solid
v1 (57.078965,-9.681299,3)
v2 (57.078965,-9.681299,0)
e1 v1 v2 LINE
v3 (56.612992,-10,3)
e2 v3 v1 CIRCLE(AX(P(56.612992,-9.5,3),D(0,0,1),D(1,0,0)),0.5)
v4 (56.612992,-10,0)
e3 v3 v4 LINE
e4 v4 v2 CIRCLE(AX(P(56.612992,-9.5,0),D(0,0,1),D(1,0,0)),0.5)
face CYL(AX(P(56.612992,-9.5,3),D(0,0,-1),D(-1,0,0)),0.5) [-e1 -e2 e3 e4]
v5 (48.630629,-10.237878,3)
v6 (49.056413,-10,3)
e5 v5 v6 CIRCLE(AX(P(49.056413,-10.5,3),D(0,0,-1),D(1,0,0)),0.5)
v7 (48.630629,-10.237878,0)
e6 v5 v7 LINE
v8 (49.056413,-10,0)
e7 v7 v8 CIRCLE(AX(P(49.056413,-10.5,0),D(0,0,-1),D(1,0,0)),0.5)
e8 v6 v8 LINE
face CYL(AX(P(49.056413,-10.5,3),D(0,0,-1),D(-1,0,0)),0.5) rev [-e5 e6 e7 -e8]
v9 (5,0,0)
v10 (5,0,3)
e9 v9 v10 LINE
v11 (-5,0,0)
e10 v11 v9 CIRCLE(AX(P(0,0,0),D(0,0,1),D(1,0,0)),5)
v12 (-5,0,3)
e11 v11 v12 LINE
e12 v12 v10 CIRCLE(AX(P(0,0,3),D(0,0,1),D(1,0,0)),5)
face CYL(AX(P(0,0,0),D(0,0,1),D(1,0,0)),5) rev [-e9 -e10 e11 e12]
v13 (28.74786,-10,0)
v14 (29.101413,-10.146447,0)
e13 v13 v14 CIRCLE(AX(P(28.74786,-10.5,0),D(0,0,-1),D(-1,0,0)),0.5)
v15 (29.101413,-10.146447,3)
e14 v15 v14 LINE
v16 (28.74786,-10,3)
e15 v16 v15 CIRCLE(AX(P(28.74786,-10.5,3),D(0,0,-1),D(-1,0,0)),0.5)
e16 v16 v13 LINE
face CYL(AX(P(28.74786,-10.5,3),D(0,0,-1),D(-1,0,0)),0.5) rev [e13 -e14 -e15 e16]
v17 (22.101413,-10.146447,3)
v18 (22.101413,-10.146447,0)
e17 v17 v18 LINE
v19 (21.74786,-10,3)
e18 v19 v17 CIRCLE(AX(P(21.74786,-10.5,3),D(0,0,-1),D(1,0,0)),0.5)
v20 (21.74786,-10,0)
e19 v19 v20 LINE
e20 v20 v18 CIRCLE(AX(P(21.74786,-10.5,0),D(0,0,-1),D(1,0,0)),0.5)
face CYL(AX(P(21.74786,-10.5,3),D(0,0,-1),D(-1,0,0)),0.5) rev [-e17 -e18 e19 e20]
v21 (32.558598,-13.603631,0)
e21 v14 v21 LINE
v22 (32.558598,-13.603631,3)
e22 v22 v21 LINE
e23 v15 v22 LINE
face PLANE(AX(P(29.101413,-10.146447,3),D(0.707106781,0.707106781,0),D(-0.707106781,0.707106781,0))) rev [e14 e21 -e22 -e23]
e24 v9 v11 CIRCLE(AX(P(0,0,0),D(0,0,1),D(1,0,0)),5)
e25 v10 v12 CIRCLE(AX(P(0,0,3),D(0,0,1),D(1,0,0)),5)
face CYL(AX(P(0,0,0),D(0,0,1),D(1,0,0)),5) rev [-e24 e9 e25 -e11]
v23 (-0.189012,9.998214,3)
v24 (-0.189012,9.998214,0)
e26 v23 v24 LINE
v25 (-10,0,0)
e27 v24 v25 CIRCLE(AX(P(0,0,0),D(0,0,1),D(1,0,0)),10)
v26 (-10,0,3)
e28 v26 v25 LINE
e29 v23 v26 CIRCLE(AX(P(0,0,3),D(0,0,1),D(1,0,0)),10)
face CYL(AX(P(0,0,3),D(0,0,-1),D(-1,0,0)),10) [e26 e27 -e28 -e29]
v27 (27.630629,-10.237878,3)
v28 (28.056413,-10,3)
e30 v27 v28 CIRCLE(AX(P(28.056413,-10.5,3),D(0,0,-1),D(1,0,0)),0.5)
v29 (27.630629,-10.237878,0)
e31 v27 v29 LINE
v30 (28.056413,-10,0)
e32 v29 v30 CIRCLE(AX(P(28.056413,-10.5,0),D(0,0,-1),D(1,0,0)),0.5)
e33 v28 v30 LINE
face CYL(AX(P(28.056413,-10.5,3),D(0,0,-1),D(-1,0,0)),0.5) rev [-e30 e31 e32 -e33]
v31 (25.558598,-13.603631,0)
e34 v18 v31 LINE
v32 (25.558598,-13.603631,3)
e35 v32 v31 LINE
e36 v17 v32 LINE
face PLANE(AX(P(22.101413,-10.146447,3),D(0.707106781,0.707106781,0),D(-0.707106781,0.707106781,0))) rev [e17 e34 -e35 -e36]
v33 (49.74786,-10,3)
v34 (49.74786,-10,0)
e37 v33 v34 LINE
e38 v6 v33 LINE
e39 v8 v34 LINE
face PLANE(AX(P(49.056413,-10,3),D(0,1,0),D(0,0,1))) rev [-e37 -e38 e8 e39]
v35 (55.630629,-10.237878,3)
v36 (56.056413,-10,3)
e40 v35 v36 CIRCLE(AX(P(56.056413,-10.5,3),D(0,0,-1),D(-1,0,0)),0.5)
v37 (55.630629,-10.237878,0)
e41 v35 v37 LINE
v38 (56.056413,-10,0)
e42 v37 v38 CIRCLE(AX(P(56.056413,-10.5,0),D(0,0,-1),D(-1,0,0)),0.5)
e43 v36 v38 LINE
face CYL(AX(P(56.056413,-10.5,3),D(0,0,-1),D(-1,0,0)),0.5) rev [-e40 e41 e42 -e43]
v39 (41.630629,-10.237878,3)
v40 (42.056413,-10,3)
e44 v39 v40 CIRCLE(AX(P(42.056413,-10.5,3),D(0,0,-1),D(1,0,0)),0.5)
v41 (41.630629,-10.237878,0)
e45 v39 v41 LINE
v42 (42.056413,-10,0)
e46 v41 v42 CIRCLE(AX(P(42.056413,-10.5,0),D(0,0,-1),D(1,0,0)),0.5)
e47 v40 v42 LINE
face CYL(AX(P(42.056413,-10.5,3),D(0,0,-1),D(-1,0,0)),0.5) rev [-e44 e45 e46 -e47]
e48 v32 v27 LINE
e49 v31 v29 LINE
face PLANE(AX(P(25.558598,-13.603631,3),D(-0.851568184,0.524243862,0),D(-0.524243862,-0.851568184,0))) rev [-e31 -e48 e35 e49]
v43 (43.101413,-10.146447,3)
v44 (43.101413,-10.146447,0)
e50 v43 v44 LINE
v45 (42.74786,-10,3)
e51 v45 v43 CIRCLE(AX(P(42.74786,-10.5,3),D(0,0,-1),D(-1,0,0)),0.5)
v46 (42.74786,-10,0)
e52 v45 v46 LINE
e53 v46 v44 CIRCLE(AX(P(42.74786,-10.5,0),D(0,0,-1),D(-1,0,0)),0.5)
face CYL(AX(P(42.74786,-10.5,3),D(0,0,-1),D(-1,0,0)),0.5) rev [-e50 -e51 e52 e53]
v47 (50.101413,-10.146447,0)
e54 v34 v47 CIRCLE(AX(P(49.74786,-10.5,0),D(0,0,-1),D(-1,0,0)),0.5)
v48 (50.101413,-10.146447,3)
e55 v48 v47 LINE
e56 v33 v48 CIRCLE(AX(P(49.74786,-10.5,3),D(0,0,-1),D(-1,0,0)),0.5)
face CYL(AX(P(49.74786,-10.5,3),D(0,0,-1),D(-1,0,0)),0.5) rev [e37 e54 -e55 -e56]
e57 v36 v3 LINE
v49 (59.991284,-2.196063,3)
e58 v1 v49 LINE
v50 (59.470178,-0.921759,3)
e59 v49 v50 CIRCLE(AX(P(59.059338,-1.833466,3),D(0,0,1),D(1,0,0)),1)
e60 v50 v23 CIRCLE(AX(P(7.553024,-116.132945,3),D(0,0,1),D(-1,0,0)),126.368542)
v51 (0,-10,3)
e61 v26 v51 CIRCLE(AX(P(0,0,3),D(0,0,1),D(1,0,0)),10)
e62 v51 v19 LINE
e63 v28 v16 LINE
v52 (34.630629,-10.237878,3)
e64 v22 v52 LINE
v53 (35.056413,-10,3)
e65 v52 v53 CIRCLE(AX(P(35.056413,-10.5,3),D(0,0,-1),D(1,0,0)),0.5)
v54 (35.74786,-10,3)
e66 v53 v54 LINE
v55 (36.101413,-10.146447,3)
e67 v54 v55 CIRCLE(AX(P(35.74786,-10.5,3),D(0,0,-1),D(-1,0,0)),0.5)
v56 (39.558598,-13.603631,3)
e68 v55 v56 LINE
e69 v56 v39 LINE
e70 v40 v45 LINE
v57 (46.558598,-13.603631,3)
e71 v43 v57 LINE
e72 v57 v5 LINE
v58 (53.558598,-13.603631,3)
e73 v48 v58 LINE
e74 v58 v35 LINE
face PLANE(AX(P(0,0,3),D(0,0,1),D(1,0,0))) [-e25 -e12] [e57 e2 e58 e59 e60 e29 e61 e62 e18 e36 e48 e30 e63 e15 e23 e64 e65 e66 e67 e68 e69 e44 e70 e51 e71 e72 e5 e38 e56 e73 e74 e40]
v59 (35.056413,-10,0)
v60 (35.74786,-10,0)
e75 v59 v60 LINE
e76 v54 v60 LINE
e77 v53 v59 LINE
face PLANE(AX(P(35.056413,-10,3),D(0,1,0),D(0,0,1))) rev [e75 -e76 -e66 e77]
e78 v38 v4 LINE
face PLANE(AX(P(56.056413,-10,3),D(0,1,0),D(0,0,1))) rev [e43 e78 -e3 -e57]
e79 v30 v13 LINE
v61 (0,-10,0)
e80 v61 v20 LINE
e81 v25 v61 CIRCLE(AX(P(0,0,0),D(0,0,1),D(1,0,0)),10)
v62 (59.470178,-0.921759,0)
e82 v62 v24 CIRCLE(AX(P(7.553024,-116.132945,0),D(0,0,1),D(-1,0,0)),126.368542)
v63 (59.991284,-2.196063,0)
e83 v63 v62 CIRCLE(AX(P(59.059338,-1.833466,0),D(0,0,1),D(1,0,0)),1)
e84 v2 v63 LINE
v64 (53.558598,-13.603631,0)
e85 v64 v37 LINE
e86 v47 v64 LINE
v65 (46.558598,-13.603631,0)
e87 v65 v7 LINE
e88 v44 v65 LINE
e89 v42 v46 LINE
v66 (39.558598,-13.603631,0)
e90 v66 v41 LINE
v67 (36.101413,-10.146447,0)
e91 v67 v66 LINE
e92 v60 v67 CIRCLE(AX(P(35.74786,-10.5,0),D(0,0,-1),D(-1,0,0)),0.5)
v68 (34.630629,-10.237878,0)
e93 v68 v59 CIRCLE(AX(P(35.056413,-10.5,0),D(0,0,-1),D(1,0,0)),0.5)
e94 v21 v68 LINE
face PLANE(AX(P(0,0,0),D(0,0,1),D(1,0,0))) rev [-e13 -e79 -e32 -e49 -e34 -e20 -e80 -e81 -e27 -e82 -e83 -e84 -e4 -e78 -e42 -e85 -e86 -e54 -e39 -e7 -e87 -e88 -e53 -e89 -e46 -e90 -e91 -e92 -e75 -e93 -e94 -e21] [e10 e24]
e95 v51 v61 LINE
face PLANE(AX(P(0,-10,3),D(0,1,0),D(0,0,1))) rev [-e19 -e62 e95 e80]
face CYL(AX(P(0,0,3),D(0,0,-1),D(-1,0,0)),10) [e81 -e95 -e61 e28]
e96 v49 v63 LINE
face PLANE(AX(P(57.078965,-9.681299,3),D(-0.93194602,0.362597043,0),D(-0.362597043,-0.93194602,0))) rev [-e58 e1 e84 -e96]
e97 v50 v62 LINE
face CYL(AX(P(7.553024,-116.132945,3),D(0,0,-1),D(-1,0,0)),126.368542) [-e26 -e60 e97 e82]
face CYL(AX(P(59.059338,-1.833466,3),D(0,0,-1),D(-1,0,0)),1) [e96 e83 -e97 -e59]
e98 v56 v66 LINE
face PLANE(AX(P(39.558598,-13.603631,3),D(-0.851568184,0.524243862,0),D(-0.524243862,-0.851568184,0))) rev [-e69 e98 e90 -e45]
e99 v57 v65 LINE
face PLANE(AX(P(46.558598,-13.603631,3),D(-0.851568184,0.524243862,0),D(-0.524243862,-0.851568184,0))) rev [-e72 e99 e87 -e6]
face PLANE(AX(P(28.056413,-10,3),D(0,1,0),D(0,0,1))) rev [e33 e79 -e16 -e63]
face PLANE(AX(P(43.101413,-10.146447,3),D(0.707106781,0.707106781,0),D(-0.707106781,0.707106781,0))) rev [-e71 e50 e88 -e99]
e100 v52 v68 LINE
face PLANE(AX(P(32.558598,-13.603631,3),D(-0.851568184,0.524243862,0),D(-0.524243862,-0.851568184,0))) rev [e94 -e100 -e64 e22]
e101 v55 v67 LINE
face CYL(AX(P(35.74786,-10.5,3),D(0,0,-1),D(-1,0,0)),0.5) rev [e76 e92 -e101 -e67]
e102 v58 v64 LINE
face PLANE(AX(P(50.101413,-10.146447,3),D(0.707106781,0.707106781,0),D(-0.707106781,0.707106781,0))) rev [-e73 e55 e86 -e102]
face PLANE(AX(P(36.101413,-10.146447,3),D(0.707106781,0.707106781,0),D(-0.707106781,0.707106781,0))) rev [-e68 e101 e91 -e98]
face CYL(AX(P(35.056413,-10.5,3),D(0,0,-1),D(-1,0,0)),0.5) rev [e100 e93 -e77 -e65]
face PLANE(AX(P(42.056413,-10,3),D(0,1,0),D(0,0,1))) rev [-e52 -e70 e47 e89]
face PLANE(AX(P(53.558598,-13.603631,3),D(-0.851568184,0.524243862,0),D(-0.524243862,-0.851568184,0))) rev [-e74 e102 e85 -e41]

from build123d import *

# Parameters (mm, degrees)
BOSS_EXTRUDE3_DEPTH = 3
SKETCH4_R           = 5
CUT_EXTRUDE1_DEPTH  = 3


with BuildPart() as part:
    # Sketch3 → Boss-Extrude3 (new body)
    with BuildSketch(Plane.XY):
        with BuildLine():
            Line((0, -10), (21.747859728, -10))
            ThreePointArc((21.747859728, -10), (21.939201445, -10.038060234), (22.101413119, -10.146446609))
            Line((22.101413119, -10.146446609), (25.558597985, -13.603631476))
            Line((25.558597985, -13.603631476), (27.630628855, -10.237878069))
            ThreePointArc((27.630628855, -10.237878069), (27.81254922, -10.063502024), (28.056412947, -10))
            Line((28.056412947, -10), (28.747859728, -10))
            ThreePointArc((28.747859728, -10), (28.939201445, -10.038060234), (29.101413119, -10.146446609))
            Line((29.101413119, -10.146446609), (32.558597985, -13.603631476))
            Line((32.558597985, -13.603631476), (34.630628855, -10.237878069))
            ThreePointArc((34.630628855, -10.237878069), (34.81254922, -10.063502024), (35.056412947, -10))
            Line((35.056412947, -10), (35.747859728, -10))
            ThreePointArc((35.747859728, -10), (35.939201445, -10.038060234), (36.101413119, -10.146446609))
            Line((36.101413119, -10.146446609), (39.558597985, -13.603631476))
            Line((39.558597985, -13.603631476), (41.630628855, -10.237878069))
            ThreePointArc((41.630628855, -10.237878069), (41.81254922, -10.063502024), (42.056412947, -10))
            Line((42.056412947, -10), (42.747859728, -10))
            ThreePointArc((42.747859728, -10), (42.939201445, -10.038060234), (43.101413119, -10.146446609))
            Line((43.101413119, -10.146446609), (46.558597985, -13.603631476))
            Line((46.558597985, -13.603631476), (48.630628855, -10.237878069))
            ThreePointArc((48.630628855, -10.237878069), (48.81254922, -10.063502024), (49.056412947, -10))
            Line((49.056412947, -10), (49.747859728, -10))
            ThreePointArc((49.747859728, -10), (49.939201445, -10.038060234), (50.101413119, -10.146446609))
            Line((50.101413119, -10.146446609), (53.558597985, -13.603631476))
            Line((53.558597985, -13.603631476), (55.630628855, -10.237878069))
            ThreePointArc((55.630628855, -10.237878069), (55.81254922, -10.063502024), (56.056412947, -10))
            Line((56.056412947, -10), (56.612992327, -10))
            ThreePointArc((56.612992327, -10), (56.895260585, -9.912704047), (57.078965337, -9.681298521))
            Line((57.078965337, -9.681298521), (59.991284364, -2.196063373))
            ThreePointArc((59.991284364, -2.196063373), (59.984936133, -1.454957765), (59.470177564, -0.921758518))
            ThreePointArc((59.470177564, -0.921758518), (30.305424132, 8.170460374), (-0.189011515, 9.998213573))
            ThreePointArc((-0.189011515, 9.998213573), (-9.999553383, -0.094509978), (0, -10))
        make_face()
    extrude(amount=BOSS_EXTRUDE3_DEPTH)

    # Sketch4 → Cut-Extrude1 (cut)
    with BuildSketch(Plane.XY.offset(3)):
        Circle(SKETCH4_R)
    extrude(amount=-CUT_EXTRUDE1_DEPTH, mode=Mode.SUBTRACT)


solid = part.part
